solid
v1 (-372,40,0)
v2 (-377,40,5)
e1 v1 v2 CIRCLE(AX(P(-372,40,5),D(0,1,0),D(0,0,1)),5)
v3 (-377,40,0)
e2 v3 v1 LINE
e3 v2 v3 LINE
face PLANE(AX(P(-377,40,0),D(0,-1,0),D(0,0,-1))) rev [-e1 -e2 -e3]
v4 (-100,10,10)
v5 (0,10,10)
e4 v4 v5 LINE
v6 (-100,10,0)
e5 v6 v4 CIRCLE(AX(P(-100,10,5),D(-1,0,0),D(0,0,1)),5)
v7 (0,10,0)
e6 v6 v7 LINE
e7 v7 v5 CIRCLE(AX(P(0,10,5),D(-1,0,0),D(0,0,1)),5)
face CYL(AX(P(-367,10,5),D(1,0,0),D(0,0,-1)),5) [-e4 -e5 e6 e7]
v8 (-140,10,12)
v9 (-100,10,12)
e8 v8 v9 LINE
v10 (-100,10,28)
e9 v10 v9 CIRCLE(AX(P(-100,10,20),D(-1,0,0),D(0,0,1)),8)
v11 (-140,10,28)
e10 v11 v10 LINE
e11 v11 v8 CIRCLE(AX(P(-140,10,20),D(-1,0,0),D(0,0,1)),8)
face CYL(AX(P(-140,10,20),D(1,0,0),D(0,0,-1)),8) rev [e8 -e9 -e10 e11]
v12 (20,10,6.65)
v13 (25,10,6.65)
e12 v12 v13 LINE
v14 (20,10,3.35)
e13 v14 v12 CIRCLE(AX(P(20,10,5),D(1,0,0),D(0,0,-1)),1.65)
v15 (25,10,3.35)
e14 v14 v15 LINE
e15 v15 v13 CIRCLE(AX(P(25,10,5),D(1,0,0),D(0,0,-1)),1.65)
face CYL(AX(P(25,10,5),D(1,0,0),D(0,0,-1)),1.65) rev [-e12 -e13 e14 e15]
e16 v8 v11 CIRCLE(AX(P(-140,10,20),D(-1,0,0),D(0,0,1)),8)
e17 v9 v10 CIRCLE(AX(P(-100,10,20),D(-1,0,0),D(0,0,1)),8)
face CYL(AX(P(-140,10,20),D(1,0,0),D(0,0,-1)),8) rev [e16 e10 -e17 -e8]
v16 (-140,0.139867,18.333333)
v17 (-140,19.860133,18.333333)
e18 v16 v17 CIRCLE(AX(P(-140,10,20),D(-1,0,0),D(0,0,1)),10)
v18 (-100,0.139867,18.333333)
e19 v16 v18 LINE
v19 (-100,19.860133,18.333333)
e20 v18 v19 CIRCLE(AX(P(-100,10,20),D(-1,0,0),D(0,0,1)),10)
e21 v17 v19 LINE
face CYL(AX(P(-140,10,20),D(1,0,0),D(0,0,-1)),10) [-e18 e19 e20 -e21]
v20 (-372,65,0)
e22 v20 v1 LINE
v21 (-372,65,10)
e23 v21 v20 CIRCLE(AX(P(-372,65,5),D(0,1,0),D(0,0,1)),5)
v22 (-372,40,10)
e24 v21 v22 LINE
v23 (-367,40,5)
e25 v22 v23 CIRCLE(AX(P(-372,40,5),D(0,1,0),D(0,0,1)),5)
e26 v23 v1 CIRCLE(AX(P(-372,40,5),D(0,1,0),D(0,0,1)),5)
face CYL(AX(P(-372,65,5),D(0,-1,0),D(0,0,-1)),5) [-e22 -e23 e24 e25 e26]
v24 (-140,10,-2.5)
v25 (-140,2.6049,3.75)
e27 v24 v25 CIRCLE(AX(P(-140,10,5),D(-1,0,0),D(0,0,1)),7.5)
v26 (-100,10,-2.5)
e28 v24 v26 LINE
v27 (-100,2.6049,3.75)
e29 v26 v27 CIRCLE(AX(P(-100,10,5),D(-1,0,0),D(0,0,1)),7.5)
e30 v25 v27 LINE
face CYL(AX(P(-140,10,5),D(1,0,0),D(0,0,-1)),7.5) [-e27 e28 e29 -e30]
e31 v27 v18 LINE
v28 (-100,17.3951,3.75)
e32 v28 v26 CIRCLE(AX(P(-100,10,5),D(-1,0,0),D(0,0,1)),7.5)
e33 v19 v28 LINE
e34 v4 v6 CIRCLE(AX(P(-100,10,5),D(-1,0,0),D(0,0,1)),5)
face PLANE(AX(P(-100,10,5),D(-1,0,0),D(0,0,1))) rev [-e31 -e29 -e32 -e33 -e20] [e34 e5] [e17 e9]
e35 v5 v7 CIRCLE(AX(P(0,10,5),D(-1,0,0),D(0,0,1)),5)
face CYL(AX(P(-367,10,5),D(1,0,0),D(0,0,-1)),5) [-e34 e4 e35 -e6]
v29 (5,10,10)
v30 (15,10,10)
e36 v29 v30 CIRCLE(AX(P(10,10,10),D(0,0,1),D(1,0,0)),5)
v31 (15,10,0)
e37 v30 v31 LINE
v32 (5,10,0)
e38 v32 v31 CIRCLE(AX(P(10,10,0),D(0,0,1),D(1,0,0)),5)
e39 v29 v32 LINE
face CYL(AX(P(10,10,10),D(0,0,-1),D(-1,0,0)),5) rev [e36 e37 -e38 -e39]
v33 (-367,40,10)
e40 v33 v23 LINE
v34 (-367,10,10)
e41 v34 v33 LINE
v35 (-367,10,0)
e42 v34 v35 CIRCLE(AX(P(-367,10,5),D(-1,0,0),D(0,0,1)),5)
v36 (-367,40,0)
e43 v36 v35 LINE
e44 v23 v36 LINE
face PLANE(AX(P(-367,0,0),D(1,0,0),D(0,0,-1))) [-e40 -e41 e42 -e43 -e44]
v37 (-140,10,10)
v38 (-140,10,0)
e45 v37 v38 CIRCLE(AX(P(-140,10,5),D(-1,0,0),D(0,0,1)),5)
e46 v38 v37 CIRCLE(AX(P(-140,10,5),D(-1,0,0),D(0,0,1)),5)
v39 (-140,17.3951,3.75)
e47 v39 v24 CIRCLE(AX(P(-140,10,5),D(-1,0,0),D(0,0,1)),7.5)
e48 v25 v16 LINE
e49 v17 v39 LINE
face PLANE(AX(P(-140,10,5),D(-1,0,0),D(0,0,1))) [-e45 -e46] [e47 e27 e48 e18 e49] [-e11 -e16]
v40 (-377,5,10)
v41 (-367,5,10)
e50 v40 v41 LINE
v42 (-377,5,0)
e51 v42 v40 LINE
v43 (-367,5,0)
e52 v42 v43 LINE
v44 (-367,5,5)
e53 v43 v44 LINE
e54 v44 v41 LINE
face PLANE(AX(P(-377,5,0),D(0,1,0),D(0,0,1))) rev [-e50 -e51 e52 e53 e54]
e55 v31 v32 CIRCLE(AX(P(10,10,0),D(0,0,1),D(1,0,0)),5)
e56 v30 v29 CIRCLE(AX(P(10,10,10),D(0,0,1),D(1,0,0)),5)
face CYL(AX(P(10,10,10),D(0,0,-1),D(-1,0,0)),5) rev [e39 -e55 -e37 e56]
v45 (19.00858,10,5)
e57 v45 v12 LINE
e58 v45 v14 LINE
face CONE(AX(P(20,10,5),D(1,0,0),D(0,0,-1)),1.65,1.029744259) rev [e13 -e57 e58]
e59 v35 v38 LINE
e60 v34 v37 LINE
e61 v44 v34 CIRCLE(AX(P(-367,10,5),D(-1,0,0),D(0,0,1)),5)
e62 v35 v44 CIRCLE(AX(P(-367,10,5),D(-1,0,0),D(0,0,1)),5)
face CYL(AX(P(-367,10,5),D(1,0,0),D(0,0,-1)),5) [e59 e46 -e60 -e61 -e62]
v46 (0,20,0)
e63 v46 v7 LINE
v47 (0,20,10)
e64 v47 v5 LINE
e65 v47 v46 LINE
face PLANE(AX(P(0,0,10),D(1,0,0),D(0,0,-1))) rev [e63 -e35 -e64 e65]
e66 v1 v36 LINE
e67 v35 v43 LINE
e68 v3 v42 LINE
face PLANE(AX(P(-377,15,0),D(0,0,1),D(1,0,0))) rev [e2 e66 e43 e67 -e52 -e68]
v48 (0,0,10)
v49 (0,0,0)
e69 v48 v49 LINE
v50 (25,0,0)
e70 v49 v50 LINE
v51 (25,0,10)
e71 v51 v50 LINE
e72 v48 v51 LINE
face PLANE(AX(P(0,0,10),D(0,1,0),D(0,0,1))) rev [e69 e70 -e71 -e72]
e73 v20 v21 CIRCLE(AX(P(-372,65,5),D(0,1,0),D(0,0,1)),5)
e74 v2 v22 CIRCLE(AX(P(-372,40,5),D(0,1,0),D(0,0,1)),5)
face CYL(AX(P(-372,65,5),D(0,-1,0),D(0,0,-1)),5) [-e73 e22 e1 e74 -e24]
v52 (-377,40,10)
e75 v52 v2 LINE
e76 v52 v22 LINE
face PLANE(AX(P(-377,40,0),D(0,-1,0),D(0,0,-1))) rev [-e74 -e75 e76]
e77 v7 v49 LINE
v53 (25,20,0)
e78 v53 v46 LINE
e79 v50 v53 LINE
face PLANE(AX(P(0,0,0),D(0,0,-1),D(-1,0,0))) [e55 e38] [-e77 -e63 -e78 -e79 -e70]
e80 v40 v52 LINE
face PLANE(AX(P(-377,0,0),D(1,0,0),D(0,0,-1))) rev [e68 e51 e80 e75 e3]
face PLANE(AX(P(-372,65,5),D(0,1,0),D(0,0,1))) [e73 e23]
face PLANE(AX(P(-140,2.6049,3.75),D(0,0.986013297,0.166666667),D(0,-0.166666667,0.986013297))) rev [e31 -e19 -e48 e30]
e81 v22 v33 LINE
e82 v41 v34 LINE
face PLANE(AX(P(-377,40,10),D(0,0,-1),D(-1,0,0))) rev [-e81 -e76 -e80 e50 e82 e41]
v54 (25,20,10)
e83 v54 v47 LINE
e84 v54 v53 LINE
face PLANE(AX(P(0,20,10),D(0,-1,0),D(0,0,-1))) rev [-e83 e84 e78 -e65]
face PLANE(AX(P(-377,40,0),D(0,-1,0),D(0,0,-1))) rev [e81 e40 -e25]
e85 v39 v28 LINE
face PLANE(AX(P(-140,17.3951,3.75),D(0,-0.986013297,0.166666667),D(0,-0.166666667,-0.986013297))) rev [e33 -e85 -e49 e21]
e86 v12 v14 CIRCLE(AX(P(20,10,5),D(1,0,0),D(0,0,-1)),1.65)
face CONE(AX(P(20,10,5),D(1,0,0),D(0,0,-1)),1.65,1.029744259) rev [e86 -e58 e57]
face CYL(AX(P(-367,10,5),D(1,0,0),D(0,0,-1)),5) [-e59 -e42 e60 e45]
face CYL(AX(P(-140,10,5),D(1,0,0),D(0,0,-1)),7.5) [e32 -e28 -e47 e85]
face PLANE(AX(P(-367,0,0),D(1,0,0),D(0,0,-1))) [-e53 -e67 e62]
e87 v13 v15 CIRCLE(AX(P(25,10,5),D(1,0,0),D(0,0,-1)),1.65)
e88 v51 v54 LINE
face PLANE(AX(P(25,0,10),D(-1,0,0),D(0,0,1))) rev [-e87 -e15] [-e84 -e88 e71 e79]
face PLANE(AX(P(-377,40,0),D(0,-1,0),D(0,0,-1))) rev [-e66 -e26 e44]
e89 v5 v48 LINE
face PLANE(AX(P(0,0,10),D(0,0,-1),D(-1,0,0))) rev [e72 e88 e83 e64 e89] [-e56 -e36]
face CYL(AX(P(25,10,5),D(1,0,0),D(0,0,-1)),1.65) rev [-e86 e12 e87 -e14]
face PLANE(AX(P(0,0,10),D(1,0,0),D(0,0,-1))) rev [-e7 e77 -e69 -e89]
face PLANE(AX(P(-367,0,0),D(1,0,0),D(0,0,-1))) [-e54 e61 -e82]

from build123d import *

# Parameters (mm, degrees)
SKETCH_6_W             = 25
SKETCH_6_H             = 20
SKETCH_6_R             = 5
EXTRUDE_4_DEPTH        = 10
SKETCH_7_R             = 5
EXTRUDE_5_DEPTH        = 367
HOLE_WIZARD_M4_1_D     = 3.3
HOLE_WIZARD_M4_1_DEPTH = 5
HOLE_WIZARD_M4_1_TIP   = 0.991420021
EXTRUDE_6_DEPTH        = 10
SKETCH_11_R            = 5
EXTRUDE_7_DEPTH        = 25
SKETCH_12_R            = 8
EXTRUDE_8_DEPTH        = 40


with BuildPart() as part:
    # 草图6 → 凸台-拉伸4 (new body)
    with BuildSketch(Plane.XY):
        with Locations((12.5, 10)):
            Rectangle(SKETCH_6_W, SKETCH_6_H)
        with Locations((10, 10)):
            Circle(SKETCH_6_R, mode=Mode.SUBTRACT)
    extrude(amount=EXTRUDE_4_DEPTH)

    # 草图7 → 凸台-拉伸5 (add)
    with BuildSketch(Plane.ZY):
        with Locations((5, 10)):
            Circle(SKETCH_7_R)
    extrude(amount=EXTRUDE_5_DEPTH)

    # M4 螺纹孔1
    with Locations(Plane(origin=(25, 0, 0), x_dir=(0, 0, -1), z_dir=(1, 0, 0))):
        with Locations((-5, 10)):
            Hole(HOLE_WIZARD_M4_1_D / 2, depth=HOLE_WIZARD_M4_1_DEPTH)
            with Locations((0, 0, -(HOLE_WIZARD_M4_1_DEPTH + HOLE_WIZARD_M4_1_TIP / 2))):  # 118° drill point
                Cone(0, HOLE_WIZARD_M4_1_D / 2, HOLE_WIZARD_M4_1_TIP, mode=Mode.SUBTRACT)

    # 草图10 → 凸台-拉伸6 (add)
    with BuildSketch(Plane.ZY.offset(367)):
        Polygon((0, 40), (10, 40), (10, 5), (0, 5), (0, 15), align=None)
    extrude(amount=EXTRUDE_6_DEPTH)

    # 草图11 → 凸台-拉伸7 (add)
    with BuildSketch(Plane(origin=(0, 40, 0), x_dir=(1, 0, 0), z_dir=(0, 1, 0))):
        with Locations(Location((-372, -5, 0), (0, 0, 270))):
            Circle(SKETCH_11_R)
    extrude(amount=EXTRUDE_7_DEPTH)

    # 草图12 → 凸台-拉伸8 (add)
    with BuildSketch(Plane.ZY.offset(100)):
        with BuildLine():
            Line((3.75, 17.395099729), (18.333333333, 19.860132972))
            ThreePointArc((18.333333333, 19.860132972), (30, 10), (18.333333333, 0.139867028))
            Line((18.333333333, 0.139867028), (3.75, 2.604900271))
            ThreePointArc((3.75, 2.604900271), (-2.5, 10), (3.75, 17.395099729))
        make_face()
        with Locations((20, 10)):
            Circle(SKETCH_12_R, mode=Mode.SUBTRACT)
    extrude(amount=EXTRUDE_8_DEPTH)


solid = part.part
